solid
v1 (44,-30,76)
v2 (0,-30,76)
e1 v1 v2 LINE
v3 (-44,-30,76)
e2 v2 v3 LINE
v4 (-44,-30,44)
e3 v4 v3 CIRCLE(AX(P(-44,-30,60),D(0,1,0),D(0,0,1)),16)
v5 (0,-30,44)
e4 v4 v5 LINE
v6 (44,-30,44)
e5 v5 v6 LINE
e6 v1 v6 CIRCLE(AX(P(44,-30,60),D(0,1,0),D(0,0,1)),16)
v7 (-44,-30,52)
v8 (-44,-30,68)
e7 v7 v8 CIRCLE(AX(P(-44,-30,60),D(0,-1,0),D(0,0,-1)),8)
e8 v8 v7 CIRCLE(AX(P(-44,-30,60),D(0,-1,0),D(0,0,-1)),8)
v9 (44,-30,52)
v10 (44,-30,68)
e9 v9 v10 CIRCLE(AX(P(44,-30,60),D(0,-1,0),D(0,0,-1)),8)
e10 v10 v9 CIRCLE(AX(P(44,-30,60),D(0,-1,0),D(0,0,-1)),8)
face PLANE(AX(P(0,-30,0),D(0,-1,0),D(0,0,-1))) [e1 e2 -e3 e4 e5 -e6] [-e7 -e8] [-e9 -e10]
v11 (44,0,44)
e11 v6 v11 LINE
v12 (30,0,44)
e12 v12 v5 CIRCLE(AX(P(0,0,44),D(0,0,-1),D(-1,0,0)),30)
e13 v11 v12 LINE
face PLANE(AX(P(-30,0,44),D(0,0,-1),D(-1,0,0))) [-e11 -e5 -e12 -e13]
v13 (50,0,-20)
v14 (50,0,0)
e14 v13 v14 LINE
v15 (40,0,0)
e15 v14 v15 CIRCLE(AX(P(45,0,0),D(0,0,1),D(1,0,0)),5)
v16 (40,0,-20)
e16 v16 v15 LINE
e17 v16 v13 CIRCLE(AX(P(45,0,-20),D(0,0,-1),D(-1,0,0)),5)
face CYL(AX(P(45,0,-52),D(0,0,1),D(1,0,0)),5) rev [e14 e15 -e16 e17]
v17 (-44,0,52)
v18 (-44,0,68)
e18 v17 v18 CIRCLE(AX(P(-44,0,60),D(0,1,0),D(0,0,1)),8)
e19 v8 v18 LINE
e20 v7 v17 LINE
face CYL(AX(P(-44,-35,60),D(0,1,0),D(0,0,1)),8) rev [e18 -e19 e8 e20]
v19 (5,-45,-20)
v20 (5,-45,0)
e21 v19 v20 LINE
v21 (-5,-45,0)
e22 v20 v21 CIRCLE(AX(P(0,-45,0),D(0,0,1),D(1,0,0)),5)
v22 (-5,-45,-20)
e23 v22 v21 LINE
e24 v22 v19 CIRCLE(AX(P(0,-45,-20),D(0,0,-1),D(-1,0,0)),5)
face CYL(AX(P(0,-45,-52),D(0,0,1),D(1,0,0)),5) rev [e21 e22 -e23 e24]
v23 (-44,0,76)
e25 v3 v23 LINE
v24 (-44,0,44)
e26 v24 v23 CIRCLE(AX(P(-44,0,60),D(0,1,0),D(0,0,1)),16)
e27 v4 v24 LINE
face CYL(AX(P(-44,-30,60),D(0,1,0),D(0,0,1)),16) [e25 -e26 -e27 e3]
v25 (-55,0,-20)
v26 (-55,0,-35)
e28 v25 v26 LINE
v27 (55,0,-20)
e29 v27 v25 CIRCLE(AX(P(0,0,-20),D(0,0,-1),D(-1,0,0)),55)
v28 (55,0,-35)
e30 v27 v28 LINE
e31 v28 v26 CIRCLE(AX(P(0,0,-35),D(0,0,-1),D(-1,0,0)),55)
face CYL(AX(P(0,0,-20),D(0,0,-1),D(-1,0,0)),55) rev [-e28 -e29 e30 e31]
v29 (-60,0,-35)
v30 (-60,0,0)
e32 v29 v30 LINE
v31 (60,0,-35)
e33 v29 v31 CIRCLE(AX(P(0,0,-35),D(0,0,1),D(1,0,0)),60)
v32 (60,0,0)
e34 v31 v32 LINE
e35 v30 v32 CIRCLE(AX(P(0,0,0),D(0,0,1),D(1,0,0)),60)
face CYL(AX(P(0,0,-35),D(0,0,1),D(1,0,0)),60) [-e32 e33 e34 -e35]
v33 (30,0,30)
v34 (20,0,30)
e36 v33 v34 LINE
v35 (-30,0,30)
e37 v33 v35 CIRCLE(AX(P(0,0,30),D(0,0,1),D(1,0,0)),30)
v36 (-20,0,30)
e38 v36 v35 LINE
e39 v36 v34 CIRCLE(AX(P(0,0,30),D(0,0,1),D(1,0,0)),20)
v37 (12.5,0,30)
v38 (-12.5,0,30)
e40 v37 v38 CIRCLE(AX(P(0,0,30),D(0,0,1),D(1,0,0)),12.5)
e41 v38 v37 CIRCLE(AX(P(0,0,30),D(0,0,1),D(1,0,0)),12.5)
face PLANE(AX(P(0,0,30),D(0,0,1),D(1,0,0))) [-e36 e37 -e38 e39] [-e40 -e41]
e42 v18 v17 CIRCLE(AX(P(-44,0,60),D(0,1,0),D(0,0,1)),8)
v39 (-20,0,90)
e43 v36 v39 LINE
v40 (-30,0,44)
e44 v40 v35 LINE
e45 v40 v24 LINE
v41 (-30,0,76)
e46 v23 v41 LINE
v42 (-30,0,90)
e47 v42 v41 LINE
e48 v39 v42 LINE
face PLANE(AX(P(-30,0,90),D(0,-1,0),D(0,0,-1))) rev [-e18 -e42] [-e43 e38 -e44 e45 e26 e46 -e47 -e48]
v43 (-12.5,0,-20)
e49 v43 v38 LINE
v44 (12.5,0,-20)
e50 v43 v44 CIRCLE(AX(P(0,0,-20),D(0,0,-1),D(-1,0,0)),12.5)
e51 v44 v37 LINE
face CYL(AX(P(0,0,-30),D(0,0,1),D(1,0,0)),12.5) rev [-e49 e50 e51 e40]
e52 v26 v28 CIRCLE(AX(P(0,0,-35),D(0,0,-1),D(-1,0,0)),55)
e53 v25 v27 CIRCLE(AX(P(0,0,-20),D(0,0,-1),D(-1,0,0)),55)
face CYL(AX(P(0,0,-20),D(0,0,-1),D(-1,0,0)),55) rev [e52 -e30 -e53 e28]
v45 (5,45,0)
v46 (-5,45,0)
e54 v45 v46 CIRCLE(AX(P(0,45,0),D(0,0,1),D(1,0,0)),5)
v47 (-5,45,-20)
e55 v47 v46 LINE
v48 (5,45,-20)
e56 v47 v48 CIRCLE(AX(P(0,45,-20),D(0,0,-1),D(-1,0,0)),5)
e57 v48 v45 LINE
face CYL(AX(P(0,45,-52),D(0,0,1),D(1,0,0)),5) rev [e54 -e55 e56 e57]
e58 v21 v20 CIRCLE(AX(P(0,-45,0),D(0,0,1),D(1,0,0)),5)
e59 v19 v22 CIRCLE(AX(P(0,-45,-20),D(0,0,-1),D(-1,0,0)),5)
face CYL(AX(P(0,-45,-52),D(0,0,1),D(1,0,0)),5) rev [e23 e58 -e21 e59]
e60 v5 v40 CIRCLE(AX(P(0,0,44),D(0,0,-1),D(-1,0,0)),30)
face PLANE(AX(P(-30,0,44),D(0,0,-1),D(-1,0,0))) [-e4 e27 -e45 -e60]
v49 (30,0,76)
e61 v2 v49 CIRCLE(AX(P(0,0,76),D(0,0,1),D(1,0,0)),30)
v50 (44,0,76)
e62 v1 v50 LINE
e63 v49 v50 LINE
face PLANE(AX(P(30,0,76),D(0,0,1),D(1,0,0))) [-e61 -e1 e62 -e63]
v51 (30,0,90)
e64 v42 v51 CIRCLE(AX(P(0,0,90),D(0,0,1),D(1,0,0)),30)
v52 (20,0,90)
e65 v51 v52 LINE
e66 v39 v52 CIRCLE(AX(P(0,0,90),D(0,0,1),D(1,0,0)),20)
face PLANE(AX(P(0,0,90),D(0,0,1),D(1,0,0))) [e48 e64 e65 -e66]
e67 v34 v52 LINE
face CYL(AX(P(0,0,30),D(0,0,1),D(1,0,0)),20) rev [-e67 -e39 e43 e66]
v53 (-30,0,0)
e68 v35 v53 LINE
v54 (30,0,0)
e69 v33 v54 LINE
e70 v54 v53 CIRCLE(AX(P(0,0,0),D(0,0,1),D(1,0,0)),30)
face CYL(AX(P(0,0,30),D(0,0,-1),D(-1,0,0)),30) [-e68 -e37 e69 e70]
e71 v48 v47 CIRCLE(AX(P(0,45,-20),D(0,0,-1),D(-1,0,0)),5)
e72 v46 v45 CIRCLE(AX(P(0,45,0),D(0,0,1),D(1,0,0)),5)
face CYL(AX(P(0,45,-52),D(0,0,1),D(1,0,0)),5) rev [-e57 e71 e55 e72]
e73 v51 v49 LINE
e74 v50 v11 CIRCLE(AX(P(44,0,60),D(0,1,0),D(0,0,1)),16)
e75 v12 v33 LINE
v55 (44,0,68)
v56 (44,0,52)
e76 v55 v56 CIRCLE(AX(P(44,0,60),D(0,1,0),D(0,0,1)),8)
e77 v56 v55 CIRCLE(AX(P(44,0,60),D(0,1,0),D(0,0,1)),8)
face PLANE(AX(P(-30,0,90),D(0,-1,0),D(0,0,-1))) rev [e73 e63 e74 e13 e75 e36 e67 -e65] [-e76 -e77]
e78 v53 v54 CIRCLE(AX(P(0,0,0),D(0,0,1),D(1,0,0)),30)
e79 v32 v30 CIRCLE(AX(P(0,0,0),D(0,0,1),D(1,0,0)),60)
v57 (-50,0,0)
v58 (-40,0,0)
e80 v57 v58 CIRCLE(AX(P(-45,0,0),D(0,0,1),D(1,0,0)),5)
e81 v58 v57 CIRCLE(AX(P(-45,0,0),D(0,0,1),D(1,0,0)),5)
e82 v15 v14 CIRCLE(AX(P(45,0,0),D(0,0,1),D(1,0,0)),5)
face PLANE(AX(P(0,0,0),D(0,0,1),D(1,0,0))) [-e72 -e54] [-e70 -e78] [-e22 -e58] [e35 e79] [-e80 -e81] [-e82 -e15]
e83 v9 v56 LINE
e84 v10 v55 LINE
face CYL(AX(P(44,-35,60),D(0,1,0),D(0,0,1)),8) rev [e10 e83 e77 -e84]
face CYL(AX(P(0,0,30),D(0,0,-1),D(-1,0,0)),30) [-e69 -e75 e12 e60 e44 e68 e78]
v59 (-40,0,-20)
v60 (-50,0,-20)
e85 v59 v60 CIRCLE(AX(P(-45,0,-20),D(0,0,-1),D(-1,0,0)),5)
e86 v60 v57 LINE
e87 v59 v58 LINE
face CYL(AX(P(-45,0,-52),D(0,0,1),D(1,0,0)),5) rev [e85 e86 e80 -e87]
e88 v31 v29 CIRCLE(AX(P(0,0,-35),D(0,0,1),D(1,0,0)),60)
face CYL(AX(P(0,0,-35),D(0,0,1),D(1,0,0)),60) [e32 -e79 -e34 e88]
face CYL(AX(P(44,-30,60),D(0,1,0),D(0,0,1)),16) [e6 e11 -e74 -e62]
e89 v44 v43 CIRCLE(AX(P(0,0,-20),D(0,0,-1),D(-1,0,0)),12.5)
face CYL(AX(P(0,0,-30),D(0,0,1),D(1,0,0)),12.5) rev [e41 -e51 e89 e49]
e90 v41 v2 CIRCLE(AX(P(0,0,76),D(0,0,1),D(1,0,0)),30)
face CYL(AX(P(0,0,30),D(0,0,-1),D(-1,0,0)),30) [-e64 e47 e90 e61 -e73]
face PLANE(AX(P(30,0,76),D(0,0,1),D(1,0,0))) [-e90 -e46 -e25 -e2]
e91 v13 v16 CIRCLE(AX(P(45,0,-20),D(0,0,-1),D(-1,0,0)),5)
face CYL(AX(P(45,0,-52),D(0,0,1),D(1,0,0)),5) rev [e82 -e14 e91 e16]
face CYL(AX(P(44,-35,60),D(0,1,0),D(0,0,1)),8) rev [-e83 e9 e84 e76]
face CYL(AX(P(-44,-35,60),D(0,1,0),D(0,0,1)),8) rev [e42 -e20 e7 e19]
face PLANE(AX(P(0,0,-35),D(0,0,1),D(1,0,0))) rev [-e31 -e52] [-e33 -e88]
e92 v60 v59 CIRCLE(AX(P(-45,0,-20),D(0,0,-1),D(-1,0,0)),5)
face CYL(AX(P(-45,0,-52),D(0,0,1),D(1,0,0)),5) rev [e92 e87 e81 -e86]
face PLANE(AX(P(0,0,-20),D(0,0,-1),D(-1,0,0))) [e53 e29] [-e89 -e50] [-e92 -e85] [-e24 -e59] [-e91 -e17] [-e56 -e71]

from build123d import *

# Parameters (mm, degrees)
FLANGE_PROFILE_R            = 60
FLANGE_120_DEPTH            = 35
HUB_PROFILE_R               = 30
HUB_DEPTH                   = 30
HALF_BEARING_SADDLE_DEPTH   = 60
FLANGE_RECESS_PROFILE_R     = 55
FLANGE_RECESS_110_DEPTH     = 15
FLANGE_BOLT_HOLES_PROFILE_R = 5
FLANGE_BOLT_HOLES_DEPTH     = 52
SADDLE_BORE_R20_DEPTH       = 60
SHAFT_BORE_PROFILE_R        = 12.5
SHAFT_BORE_25_DEPTH         = 60
MOUNTING_LUG_A_DEPTH        = 30
MOUNTING_LUG_B_DEPTH        = 30
LUG_BRIDGE_PROFILE_W        = 60
LUG_BRIDGE_PROFILE_H        = 32
LUG_BRIDGE_DEPTH            = 30
BRIDGE_BORE_RELIEF_DEPTH    = 35
LUG_HOLES_PROFILE_R         = 8
LUG_HOLES_2X_16_DEPTH       = 35


with BuildPart() as part:
    # Flange Profile → Flange Ø120 (new body)
    with BuildSketch(Plane.XY):
        Circle(FLANGE_PROFILE_R)
    extrude(amount=-FLANGE_120_DEPTH)

    # Hub Profile → Hub (add)
    with BuildSketch(Plane.XY):
        Circle(HUB_PROFILE_R)
    extrude(amount=HUB_DEPTH)

    # Saddle Profile → Half-Bearing Saddle (add)
    with BuildSketch(Plane.XY.offset(30)):
        with BuildLine():
            Line((-30, 0), (30, 0))
            ThreePointArc((30, 0), (0, -30), (-30, 0))
        make_face()
    extrude(amount=HALF_BEARING_SADDLE_DEPTH)

    # Flange Recess Profile → Flange Recess Ø110 (cut)
    with BuildSketch(Plane(origin=(0, 0, -35), x_dir=(-1, 0, 0), z_dir=(0, 0, -1))):
        Circle(FLANGE_RECESS_PROFILE_R)
    extrude(amount=-FLANGE_RECESS_110_DEPTH, mode=Mode.SUBTRACT)

    # Flange Bolt Holes Profile → Flange Bolt Holes (cut)
    with BuildSketch(Plane.XY):
        with Locations((45, 0)):
            Circle(FLANGE_BOLT_HOLES_PROFILE_R)
        with Locations((0, 45)):
            Circle(FLANGE_BOLT_HOLES_PROFILE_R)
        with Locations((-45, 0)):
            Circle(FLANGE_BOLT_HOLES_PROFILE_R)
        with Locations((0, -45)):
            Circle(FLANGE_BOLT_HOLES_PROFILE_R)
    extrude(amount=-FLANGE_BOLT_HOLES_DEPTH, mode=Mode.SUBTRACT)

    # Saddle Bore Profile → Saddle Bore R20 (cut)
    with BuildSketch(Plane.XY.offset(90)):
        with BuildLine():
            Line((-20, 0), (20, 0))
            ThreePointArc((20, 0), (0, -20), (-20, 0))
        make_face()
    extrude(amount=-SADDLE_BORE_R20_DEPTH, mode=Mode.SUBTRACT)

    # Shaft Bore Profile → Shaft Bore Ø25 (cut)
    with BuildSketch(Plane.XY.offset(30)):
        Circle(SHAFT_BORE_PROFILE_R)
    extrude(amount=-SHAFT_BORE_25_DEPTH, mode=Mode.SUBTRACT)



with BuildPart() as body_2:
    # Mounting Lug A Profile → Mounting Lug A (new body)
    with BuildSketch(Plane(origin=(0, 0, 0), x_dir=(1, 0, 0), z_dir=(0, 1, 0))):
        with BuildLine():
            Line((-44, -76), (-30, -76))
            Line((-30, -76), (-30, -44))
            Line((-30, -44), (-44, -44))
            ThreePointArc((-44, -44), (-60, -60), (-44, -76))
        make_face()
    extrude(amount=-MOUNTING_LUG_A_DEPTH)


with BuildPart() as body_3:
    # Mounting Lug B Profile → Mounting Lug B (new body)
    with BuildSketch(Plane(origin=(0, 0, 0), x_dir=(1, 0, 0), z_dir=(0, 1, 0))):
        with BuildLine():
            Line((44, -44), (30, -44))
            Line((30, -44), (30, -76))
            Line((30, -76), (44, -76))
            ThreePointArc((44, -76), (60, -60), (44, -44))
        make_face()
    extrude(amount=-MOUNTING_LUG_B_DEPTH)


with BuildPart() as part_1:
    add(part.part)

    add(body_2.part)  # Lug Bridge merges body 2

    add(body_3.part)  # Lug Bridge merges body 3
    # Lug Bridge Profile → Lug Bridge (add)
    with BuildSketch(Plane.XZ.offset(30)):
        with Locations((0, 60)):
            Rectangle(LUG_BRIDGE_PROFILE_W, LUG_BRIDGE_PROFILE_H)
    extrude(amount=-LUG_BRIDGE_DEPTH)

    # Bridge Relief Profile → Bridge Bore Relief (cut)
    with BuildSketch(Plane.XY.offset(76)):
        with BuildLine():
            Line((-20, 0), (20, 0))
            ThreePointArc((20, 0), (0, -20), (-20, 0))
        make_face()
    extrude(amount=-BRIDGE_BORE_RELIEF_DEPTH, mode=Mode.SUBTRACT)

    # Lug Holes Profile → Lug Holes 2xØ16 (cut)
    with BuildSketch(Plane(origin=(0, 0, 0), x_dir=(1, 0, 0), z_dir=(0, 1, 0))):
        with Locations(Location((-44, -60, 0), (0, 0, 270))):
            Circle(LUG_HOLES_PROFILE_R)
        with Locations(Location((44, -60, 0), (0, 0, 270))):
            Circle(LUG_HOLES_PROFILE_R)
    extrude(amount=-LUG_HOLES_2X_16_DEPTH, mode=Mode.SUBTRACT)


solid = part_1.part
